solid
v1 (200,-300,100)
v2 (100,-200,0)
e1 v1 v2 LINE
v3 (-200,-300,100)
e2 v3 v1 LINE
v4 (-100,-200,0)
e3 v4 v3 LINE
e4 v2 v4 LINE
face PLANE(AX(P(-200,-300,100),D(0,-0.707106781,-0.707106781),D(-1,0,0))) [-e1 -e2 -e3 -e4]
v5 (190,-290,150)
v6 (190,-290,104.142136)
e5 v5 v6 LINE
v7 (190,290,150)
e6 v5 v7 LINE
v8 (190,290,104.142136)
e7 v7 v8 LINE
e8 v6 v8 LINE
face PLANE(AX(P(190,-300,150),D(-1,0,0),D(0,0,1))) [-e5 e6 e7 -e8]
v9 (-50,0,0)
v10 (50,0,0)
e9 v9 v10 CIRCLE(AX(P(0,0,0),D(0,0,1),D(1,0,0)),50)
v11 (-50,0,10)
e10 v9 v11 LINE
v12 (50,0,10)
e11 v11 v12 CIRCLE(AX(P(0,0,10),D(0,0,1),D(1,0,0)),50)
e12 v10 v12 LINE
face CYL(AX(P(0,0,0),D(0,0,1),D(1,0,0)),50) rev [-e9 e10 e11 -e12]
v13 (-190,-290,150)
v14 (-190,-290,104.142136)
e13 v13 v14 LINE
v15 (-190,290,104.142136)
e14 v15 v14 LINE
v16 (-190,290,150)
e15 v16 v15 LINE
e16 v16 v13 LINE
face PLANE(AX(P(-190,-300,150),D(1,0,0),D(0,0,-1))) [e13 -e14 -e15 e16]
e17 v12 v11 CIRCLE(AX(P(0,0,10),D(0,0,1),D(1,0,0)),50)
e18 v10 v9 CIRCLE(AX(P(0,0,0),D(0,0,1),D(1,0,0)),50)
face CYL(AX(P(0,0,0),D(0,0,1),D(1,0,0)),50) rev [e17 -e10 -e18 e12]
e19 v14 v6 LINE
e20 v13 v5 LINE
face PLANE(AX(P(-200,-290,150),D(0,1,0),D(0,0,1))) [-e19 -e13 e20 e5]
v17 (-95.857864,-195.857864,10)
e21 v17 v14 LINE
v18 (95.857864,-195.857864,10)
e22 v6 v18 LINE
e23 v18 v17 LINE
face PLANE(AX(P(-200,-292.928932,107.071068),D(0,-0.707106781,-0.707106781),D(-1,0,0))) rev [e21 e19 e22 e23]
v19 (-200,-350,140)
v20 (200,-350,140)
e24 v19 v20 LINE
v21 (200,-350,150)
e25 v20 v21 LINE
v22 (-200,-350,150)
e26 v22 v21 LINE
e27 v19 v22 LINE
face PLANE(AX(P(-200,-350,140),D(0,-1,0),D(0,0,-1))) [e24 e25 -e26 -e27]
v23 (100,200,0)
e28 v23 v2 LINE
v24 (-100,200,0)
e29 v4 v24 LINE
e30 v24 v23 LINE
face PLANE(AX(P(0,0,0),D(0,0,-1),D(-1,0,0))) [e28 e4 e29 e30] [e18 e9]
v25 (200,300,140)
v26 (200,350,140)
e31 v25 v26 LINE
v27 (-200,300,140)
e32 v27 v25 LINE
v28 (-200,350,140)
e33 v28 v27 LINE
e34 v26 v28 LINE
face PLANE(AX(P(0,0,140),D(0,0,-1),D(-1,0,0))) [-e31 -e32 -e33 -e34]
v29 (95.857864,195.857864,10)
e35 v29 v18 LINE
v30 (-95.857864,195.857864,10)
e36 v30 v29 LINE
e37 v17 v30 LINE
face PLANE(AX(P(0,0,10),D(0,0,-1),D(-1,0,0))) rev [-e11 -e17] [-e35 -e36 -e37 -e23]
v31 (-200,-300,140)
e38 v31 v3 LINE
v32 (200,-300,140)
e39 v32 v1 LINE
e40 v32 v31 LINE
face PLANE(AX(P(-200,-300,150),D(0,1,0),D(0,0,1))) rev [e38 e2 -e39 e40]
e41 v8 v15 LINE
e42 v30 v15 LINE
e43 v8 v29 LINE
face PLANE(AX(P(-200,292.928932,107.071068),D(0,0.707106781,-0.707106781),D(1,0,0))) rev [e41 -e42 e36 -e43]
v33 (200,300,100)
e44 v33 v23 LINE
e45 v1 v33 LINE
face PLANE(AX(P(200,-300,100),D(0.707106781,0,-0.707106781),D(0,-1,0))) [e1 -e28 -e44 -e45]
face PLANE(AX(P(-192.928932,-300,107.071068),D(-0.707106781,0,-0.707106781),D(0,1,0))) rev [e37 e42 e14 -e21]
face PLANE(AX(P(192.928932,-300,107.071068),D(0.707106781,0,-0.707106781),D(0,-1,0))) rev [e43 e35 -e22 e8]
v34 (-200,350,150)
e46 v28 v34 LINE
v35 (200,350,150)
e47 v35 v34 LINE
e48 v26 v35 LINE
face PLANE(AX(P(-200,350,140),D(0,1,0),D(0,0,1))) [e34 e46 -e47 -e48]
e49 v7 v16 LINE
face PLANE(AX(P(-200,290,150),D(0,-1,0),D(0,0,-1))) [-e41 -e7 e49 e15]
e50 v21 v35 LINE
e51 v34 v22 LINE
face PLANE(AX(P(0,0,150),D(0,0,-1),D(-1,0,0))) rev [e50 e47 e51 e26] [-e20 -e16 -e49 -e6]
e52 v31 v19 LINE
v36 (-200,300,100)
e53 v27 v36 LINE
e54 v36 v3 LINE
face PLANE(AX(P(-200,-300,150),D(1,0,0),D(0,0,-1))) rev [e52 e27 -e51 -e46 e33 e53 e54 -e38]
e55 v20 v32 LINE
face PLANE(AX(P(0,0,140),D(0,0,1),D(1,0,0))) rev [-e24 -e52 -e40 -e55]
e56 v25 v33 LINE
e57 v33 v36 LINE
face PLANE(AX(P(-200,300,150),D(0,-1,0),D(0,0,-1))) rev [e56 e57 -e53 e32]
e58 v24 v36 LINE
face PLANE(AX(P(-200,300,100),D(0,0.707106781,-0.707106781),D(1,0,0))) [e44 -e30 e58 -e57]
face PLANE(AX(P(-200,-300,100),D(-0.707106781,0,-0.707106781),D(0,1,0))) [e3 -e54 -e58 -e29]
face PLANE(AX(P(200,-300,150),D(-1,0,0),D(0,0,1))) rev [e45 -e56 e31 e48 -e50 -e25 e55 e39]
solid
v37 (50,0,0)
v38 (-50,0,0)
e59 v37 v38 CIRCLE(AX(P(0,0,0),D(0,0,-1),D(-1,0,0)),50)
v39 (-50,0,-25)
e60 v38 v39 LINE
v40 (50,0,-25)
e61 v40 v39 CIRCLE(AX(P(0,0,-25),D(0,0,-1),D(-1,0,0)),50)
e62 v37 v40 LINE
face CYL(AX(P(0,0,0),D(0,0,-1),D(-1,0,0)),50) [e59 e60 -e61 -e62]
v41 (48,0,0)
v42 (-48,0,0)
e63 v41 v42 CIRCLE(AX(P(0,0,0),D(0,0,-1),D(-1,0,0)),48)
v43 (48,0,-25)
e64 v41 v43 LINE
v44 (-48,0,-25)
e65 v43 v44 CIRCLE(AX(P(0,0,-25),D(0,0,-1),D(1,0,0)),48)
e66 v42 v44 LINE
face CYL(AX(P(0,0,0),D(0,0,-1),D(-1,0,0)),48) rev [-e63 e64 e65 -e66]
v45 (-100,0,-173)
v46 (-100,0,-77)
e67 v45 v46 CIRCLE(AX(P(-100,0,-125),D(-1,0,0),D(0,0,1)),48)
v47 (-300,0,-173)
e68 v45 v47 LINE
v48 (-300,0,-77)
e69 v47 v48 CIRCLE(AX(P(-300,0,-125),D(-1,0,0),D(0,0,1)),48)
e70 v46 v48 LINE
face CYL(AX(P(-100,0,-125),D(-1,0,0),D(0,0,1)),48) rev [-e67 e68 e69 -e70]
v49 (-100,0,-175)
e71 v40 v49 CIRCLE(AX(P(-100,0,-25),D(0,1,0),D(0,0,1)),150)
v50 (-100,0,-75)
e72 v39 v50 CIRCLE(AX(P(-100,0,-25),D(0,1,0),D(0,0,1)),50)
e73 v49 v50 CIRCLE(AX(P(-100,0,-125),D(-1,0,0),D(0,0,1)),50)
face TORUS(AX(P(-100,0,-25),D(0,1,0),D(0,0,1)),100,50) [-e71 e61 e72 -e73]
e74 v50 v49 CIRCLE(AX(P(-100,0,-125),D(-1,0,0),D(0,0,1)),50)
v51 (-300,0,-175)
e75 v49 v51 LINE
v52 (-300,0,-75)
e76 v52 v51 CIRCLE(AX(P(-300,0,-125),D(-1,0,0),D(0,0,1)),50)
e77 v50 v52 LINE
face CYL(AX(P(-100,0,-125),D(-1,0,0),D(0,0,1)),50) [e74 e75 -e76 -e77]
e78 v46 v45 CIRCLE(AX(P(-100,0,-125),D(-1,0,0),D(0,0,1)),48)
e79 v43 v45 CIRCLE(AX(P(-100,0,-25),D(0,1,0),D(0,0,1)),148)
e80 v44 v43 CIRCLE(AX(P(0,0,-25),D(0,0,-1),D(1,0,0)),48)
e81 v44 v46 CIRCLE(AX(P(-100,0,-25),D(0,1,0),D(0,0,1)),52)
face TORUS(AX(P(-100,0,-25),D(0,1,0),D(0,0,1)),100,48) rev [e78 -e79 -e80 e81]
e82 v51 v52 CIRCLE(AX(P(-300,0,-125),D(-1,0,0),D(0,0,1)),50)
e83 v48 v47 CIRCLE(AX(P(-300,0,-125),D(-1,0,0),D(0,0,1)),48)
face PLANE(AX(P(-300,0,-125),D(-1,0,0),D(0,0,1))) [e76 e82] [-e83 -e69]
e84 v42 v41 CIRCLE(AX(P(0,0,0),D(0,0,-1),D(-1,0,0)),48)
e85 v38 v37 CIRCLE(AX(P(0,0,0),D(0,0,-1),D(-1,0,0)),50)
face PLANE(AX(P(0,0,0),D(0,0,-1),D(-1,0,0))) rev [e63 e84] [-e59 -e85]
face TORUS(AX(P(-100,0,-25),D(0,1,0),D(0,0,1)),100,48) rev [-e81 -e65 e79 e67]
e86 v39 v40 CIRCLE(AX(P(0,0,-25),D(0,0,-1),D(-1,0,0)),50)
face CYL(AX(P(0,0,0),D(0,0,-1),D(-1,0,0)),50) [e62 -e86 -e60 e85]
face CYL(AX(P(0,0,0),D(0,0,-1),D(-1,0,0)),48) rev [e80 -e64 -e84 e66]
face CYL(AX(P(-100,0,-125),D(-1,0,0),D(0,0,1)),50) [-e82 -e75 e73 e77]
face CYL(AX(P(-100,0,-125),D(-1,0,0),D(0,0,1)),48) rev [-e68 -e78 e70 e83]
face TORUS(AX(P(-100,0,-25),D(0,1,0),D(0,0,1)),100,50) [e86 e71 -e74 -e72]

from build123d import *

# Parameters (mm, degrees)
SKETCH_1_W          = 400
SKETCH_1_H          = 600
EXTRUDE_1_DEPTH     = 150
CHAMFER_2_SIZE      = 100
SHELL_1_T           = -10
SKETCH_4_R          = 50
CUT_EXTRUDE_2_DEPTH = 387.781592116
SKETCH_6_R          = 50
SHELL_2_T           = -2
SKETCH_7_W          = 400
SKETCH_7_H          = 50
EXTRUDE_3_DEPTH     = 10


with BuildPart() as part:
    # 草图1 → 凸台-拉伸1 (new body)
    with BuildSketch(Plane.XY):
        Rectangle(SKETCH_1_W, SKETCH_1_H)
    extrude(amount=EXTRUDE_1_DEPTH)

    # 倒角2
    chamfer_2_edges = [part.edges().sort_by_distance(p)[0] for p in [
        (0, -300, 0),
        (-200, 0, 0),
        (0, 300, 0),
        (200, 0, 0),
    ]]
    chamfer(chamfer_2_edges, length=CHAMFER_2_SIZE)

    # 抽壳1
    shell_1_openings = [part.faces().sort_by_distance(p)[0] for p in [
        (0, 0, 150),
    ]]
    offset(amount=SHELL_1_T, openings=shell_1_openings, kind=Kind.INTERSECTION)

    # 草图4 → 切除-拉伸2 (cut, through all)
    with BuildSketch(Plane.XY.offset(10)):
        Circle(SKETCH_4_R)
    extrude(amount=-CUT_EXTRUDE_2_DEPTH, mode=Mode.SUBTRACT)

    # 草图7 → 凸台-拉伸3 (add)
    with BuildSketch(Plane.XY.offset(150)):
        with Locations((0, 325)):
            Rectangle(SKETCH_7_W, SKETCH_7_H)
        with Locations((0, -325)):
            Rectangle(SKETCH_7_W, SKETCH_7_H)
    extrude(amount=-EXTRUDE_3_DEPTH)


with BuildPart() as body_2:
    # 扫描1: sweep along a path in 草图5
    with BuildLine(Plane(origin=(0, 0, 0), x_dir=(1, 0, 0), z_dir=(0, 1, 0))) as sweep_1_path:
        Line((0, 0), (0, 25))
        ThreePointArc((0, 25), (-29.289321881, 95.710678119), (-100, 125))
        Line((-100, 125), (-300, 125))
    # 草图6 → 扫描1 (sweep)
    with BuildSketch(Plane(origin=(0, 0, 0), x_dir=(-1, 0, 0), z_dir=(0, 0, -1))):
        Circle(SKETCH_6_R)
    sweep(path=sweep_1_path.line)

    # 抽壳2
    shell_2_openings = [body_2.faces().sort_by_distance(p)[0] for p in [
        (-300, 0, -125),
        (0, 0, 0),
    ]]
    offset(amount=SHELL_2_T, openings=shell_2_openings, kind=Kind.INTERSECTION)


solid = Compound([part.part, body_2.part])
